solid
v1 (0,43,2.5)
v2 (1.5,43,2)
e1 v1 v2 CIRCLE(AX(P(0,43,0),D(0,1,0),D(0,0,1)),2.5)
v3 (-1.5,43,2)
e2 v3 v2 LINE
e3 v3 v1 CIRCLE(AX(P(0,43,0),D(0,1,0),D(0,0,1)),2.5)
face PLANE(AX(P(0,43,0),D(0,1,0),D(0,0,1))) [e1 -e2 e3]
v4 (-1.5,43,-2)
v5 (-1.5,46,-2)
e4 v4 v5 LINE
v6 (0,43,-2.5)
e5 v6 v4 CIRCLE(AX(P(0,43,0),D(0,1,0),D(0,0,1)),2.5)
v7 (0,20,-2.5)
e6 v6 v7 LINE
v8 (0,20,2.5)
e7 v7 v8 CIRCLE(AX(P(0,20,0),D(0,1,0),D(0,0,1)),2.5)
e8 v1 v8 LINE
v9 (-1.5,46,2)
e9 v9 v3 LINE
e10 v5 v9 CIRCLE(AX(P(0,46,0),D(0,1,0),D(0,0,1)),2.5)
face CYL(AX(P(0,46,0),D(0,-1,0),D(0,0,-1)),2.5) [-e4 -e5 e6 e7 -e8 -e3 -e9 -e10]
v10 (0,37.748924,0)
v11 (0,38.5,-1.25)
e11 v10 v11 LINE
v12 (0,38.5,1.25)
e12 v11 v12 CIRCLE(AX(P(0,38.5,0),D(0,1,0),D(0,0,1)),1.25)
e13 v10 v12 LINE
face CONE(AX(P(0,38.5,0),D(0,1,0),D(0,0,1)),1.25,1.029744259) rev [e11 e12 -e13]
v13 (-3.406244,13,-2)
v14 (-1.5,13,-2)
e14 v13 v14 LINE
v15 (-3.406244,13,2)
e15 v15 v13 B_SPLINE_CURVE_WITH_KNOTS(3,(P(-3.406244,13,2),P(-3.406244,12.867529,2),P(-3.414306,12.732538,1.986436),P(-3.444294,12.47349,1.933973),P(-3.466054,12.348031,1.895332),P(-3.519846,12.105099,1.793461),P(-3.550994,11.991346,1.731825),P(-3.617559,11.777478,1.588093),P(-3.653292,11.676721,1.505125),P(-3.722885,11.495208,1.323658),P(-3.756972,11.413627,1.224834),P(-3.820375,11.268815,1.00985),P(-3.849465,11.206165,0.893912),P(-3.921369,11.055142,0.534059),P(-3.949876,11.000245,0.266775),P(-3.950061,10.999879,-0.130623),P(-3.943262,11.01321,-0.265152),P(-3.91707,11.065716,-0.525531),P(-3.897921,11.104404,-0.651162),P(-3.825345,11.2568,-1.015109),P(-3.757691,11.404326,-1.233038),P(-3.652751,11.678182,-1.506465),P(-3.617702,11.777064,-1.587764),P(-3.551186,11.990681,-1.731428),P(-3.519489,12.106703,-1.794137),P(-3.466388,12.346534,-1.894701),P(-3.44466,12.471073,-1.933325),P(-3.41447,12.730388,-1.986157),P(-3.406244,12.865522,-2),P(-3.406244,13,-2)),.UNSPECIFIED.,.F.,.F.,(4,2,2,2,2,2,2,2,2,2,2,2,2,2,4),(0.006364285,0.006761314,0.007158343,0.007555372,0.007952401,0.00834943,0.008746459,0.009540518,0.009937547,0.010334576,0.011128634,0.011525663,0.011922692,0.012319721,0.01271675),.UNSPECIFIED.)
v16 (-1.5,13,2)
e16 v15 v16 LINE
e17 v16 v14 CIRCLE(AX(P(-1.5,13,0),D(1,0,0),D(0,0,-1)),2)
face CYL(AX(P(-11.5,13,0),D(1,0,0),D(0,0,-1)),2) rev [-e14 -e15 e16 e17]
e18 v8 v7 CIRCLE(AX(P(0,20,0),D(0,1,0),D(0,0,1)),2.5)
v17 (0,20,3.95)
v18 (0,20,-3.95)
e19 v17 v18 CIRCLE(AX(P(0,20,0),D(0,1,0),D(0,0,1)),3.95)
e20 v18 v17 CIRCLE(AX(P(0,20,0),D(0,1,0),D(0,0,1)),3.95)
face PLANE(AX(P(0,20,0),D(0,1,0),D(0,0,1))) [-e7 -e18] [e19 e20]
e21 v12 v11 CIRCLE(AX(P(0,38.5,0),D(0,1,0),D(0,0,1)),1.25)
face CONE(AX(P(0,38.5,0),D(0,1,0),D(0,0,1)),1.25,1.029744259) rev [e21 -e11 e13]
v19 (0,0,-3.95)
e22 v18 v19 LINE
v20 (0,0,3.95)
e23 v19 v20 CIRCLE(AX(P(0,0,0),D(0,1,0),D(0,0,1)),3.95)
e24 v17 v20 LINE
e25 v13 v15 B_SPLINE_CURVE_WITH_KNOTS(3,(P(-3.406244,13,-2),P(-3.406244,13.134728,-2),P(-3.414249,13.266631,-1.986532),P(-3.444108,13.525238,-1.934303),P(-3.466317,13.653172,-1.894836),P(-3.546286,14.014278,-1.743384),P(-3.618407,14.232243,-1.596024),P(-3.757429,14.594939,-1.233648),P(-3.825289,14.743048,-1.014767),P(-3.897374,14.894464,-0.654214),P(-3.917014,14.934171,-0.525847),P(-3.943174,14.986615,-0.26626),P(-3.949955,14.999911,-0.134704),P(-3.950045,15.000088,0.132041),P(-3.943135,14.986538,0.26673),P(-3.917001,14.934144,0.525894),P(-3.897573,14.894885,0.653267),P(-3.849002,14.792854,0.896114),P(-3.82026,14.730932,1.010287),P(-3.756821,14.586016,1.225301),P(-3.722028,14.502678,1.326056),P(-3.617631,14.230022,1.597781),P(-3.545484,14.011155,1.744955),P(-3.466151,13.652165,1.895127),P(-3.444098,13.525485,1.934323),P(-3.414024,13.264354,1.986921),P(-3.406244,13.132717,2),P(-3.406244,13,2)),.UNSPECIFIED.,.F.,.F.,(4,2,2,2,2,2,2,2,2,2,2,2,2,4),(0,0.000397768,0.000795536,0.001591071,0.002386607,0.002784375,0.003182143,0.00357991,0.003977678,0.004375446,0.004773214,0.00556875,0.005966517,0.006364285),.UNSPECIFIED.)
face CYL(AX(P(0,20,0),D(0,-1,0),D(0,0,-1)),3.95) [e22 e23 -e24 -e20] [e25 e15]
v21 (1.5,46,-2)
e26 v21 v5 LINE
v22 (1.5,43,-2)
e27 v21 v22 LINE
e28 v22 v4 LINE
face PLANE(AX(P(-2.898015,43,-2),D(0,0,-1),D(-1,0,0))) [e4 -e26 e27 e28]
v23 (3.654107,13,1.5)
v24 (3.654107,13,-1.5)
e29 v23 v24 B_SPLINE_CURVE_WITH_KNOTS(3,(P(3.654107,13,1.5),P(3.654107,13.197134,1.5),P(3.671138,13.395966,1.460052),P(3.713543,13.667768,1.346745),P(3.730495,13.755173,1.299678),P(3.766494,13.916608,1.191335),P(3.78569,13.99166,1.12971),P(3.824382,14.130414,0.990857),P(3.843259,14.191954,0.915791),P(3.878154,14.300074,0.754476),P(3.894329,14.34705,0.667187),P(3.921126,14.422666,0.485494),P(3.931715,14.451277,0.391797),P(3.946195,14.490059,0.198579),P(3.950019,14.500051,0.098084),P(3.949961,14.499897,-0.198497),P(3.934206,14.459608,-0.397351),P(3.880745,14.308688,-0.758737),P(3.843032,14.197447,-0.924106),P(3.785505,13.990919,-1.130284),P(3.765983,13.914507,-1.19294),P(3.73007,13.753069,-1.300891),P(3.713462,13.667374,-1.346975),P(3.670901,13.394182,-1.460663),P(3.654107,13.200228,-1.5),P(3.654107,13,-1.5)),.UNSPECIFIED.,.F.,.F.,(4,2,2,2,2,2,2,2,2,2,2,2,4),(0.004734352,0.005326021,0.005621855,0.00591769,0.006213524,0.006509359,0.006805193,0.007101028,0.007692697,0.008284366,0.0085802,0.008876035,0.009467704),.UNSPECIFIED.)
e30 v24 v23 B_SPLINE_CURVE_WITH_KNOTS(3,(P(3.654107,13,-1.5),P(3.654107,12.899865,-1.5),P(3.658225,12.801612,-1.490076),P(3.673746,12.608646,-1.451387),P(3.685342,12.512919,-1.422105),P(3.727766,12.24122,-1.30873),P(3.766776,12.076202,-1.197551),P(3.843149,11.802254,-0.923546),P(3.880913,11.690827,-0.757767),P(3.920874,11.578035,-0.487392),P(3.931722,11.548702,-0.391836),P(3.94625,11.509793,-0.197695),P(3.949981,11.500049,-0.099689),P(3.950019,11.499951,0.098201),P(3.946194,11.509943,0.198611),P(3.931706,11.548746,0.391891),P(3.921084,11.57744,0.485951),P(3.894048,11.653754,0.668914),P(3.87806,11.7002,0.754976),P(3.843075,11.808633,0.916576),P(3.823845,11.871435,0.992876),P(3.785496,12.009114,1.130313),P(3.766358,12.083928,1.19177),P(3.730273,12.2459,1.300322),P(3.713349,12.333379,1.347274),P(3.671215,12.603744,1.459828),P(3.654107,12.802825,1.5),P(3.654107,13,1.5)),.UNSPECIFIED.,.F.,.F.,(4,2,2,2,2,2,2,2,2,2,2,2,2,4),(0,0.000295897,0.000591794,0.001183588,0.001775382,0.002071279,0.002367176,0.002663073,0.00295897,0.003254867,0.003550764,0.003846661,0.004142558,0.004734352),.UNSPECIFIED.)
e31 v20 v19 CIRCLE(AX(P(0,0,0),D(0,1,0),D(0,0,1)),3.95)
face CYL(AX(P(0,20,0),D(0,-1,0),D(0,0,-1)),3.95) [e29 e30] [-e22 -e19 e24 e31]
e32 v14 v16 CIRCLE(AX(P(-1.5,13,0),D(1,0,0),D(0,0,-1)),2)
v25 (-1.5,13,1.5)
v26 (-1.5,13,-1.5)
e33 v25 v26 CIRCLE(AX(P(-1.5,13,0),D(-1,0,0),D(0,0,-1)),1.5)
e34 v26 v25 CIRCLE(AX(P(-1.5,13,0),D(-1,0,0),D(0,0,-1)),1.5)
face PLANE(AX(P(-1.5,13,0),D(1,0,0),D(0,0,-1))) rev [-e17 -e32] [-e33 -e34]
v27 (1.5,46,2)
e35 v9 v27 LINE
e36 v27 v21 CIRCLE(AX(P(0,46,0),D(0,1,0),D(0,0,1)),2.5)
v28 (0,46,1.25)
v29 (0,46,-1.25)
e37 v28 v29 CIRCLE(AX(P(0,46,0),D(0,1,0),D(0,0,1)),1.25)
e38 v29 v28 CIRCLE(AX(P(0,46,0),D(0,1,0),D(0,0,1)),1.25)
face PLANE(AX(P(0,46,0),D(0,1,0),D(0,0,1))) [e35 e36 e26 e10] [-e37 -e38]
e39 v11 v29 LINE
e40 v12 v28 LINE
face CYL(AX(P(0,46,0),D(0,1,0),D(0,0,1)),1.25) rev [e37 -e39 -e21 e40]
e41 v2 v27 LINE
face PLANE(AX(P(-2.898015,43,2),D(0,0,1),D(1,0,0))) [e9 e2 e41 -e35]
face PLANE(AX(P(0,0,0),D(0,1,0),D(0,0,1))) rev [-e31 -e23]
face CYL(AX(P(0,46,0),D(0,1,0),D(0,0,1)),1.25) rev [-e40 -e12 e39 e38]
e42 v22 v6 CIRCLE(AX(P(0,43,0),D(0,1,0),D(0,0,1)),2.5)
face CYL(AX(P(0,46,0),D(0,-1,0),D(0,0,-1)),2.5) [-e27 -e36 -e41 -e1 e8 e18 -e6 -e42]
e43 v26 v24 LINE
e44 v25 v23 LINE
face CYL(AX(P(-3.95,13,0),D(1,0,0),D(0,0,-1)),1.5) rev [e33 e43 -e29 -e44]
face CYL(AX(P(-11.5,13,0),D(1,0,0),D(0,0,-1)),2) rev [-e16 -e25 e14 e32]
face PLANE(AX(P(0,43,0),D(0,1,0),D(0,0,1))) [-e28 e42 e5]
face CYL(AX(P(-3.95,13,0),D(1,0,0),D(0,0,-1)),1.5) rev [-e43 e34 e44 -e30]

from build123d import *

# Parameters (mm, degrees)
SKETCH1_R               = 3.95
BOSS_EXTRUDE1_DEPTH     = 20
SKETCH2_R               = 2.5
BOSS_EXTRUDE2_DEPTH     = 26
SKETCH3_OUTSIDE_W       = 19.368
SKETCH3_OUTSIDE_H       = 19.368
SKETCH3_OUTSIDE_W_2     = 5.796030148
SKETCH3_OUTSIDE_H_2     = 4
CUT_EXTRUDE1_DEPTH      = 3
CUT_EXTRUDE2_DEPTH      = 47.337943416
CUT_EXTRUDE2_DEPTH_BACK = 47.337943416
SKETCH4_R               = 1.5
CUT_EXTRUDE3_START      = -1.5
SKETCH5_R               = 2
CUT_EXTRUDE3_DEPTH      = 10


with BuildPart() as part:
    # Sketch1 → Boss-Extrude1 (new body)
    with BuildSketch(Plane(origin=(0, 0, 0), x_dir=(1, 0, 0), z_dir=(0, 1, 0))):
        with Locations(Location((0, 0, 0), (0, 0, 270))):
            Circle(SKETCH1_R)
    extrude(amount=BOSS_EXTRUDE1_DEPTH)

    # Sketch2 → Boss-Extrude2 (add)
    with BuildSketch(Plane(origin=(0, 20, 0), x_dir=(1, 0, 0), z_dir=(0, 1, 0))):
        with Locations(Location((0, 0, 0), (0, 0, 90))):
            Circle(SKETCH2_R)
    extrude(amount=BOSS_EXTRUDE2_DEPTH)

    # Sketch3 outside → Cut-Extrude1 (cut)
    with BuildSketch(Plane(origin=(0, 46, 0), x_dir=(1, 0, 0), z_dir=(0, 1, 0))):
        Rectangle(SKETCH3_OUTSIDE_W, SKETCH3_OUTSIDE_H)
        Rectangle(SKETCH3_OUTSIDE_W_2, SKETCH3_OUTSIDE_H_2, mode=Mode.SUBTRACT)
    extrude(amount=-CUT_EXTRUDE1_DEPTH, mode=Mode.SUBTRACT)

    # Sketch4 → Cut-Extrude2 (cut, two sides: drawn at the far end of the back side and taken through both)
    with BuildSketch(Plane(origin=(0, 0, 0), x_dir=(0, 0, -1), z_dir=(1, 0, 0)).offset(-CUT_EXTRUDE2_DEPTH_BACK)):
        with Locations((0, 13)):
            Circle(SKETCH4_R)
    extrude(amount=CUT_EXTRUDE2_DEPTH + CUT_EXTRUDE2_DEPTH_BACK, mode=Mode.SUBTRACT)

    # Sketch5 → Cut-Extrude3 (cut)
    with BuildSketch(Plane(origin=(0, 0, 0), x_dir=(0, 0, -1), z_dir=(1, 0, 0)).offset(CUT_EXTRUDE3_START)):
        with Locations((0, 13)):
            Circle(SKETCH5_R)
    extrude(amount=-CUT_EXTRUDE3_DEPTH, mode=Mode.SUBTRACT)

    # Sketch6 → M3 Tapped Hole2 (revolve, cut)
    with BuildSketch(Plane(origin=(0, 46, 0), x_dir=(0, 0, 1), z_dir=(1, 0, 0))):
        Polygon((0, 0), (0, 8.251075774), (1.25, 7.5), (1.25, 0), align=None)
    revolve(axis=Axis((0, 52.35, 0), (0, -1, 0)), mode=Mode.SUBTRACT)


solid = part.part
